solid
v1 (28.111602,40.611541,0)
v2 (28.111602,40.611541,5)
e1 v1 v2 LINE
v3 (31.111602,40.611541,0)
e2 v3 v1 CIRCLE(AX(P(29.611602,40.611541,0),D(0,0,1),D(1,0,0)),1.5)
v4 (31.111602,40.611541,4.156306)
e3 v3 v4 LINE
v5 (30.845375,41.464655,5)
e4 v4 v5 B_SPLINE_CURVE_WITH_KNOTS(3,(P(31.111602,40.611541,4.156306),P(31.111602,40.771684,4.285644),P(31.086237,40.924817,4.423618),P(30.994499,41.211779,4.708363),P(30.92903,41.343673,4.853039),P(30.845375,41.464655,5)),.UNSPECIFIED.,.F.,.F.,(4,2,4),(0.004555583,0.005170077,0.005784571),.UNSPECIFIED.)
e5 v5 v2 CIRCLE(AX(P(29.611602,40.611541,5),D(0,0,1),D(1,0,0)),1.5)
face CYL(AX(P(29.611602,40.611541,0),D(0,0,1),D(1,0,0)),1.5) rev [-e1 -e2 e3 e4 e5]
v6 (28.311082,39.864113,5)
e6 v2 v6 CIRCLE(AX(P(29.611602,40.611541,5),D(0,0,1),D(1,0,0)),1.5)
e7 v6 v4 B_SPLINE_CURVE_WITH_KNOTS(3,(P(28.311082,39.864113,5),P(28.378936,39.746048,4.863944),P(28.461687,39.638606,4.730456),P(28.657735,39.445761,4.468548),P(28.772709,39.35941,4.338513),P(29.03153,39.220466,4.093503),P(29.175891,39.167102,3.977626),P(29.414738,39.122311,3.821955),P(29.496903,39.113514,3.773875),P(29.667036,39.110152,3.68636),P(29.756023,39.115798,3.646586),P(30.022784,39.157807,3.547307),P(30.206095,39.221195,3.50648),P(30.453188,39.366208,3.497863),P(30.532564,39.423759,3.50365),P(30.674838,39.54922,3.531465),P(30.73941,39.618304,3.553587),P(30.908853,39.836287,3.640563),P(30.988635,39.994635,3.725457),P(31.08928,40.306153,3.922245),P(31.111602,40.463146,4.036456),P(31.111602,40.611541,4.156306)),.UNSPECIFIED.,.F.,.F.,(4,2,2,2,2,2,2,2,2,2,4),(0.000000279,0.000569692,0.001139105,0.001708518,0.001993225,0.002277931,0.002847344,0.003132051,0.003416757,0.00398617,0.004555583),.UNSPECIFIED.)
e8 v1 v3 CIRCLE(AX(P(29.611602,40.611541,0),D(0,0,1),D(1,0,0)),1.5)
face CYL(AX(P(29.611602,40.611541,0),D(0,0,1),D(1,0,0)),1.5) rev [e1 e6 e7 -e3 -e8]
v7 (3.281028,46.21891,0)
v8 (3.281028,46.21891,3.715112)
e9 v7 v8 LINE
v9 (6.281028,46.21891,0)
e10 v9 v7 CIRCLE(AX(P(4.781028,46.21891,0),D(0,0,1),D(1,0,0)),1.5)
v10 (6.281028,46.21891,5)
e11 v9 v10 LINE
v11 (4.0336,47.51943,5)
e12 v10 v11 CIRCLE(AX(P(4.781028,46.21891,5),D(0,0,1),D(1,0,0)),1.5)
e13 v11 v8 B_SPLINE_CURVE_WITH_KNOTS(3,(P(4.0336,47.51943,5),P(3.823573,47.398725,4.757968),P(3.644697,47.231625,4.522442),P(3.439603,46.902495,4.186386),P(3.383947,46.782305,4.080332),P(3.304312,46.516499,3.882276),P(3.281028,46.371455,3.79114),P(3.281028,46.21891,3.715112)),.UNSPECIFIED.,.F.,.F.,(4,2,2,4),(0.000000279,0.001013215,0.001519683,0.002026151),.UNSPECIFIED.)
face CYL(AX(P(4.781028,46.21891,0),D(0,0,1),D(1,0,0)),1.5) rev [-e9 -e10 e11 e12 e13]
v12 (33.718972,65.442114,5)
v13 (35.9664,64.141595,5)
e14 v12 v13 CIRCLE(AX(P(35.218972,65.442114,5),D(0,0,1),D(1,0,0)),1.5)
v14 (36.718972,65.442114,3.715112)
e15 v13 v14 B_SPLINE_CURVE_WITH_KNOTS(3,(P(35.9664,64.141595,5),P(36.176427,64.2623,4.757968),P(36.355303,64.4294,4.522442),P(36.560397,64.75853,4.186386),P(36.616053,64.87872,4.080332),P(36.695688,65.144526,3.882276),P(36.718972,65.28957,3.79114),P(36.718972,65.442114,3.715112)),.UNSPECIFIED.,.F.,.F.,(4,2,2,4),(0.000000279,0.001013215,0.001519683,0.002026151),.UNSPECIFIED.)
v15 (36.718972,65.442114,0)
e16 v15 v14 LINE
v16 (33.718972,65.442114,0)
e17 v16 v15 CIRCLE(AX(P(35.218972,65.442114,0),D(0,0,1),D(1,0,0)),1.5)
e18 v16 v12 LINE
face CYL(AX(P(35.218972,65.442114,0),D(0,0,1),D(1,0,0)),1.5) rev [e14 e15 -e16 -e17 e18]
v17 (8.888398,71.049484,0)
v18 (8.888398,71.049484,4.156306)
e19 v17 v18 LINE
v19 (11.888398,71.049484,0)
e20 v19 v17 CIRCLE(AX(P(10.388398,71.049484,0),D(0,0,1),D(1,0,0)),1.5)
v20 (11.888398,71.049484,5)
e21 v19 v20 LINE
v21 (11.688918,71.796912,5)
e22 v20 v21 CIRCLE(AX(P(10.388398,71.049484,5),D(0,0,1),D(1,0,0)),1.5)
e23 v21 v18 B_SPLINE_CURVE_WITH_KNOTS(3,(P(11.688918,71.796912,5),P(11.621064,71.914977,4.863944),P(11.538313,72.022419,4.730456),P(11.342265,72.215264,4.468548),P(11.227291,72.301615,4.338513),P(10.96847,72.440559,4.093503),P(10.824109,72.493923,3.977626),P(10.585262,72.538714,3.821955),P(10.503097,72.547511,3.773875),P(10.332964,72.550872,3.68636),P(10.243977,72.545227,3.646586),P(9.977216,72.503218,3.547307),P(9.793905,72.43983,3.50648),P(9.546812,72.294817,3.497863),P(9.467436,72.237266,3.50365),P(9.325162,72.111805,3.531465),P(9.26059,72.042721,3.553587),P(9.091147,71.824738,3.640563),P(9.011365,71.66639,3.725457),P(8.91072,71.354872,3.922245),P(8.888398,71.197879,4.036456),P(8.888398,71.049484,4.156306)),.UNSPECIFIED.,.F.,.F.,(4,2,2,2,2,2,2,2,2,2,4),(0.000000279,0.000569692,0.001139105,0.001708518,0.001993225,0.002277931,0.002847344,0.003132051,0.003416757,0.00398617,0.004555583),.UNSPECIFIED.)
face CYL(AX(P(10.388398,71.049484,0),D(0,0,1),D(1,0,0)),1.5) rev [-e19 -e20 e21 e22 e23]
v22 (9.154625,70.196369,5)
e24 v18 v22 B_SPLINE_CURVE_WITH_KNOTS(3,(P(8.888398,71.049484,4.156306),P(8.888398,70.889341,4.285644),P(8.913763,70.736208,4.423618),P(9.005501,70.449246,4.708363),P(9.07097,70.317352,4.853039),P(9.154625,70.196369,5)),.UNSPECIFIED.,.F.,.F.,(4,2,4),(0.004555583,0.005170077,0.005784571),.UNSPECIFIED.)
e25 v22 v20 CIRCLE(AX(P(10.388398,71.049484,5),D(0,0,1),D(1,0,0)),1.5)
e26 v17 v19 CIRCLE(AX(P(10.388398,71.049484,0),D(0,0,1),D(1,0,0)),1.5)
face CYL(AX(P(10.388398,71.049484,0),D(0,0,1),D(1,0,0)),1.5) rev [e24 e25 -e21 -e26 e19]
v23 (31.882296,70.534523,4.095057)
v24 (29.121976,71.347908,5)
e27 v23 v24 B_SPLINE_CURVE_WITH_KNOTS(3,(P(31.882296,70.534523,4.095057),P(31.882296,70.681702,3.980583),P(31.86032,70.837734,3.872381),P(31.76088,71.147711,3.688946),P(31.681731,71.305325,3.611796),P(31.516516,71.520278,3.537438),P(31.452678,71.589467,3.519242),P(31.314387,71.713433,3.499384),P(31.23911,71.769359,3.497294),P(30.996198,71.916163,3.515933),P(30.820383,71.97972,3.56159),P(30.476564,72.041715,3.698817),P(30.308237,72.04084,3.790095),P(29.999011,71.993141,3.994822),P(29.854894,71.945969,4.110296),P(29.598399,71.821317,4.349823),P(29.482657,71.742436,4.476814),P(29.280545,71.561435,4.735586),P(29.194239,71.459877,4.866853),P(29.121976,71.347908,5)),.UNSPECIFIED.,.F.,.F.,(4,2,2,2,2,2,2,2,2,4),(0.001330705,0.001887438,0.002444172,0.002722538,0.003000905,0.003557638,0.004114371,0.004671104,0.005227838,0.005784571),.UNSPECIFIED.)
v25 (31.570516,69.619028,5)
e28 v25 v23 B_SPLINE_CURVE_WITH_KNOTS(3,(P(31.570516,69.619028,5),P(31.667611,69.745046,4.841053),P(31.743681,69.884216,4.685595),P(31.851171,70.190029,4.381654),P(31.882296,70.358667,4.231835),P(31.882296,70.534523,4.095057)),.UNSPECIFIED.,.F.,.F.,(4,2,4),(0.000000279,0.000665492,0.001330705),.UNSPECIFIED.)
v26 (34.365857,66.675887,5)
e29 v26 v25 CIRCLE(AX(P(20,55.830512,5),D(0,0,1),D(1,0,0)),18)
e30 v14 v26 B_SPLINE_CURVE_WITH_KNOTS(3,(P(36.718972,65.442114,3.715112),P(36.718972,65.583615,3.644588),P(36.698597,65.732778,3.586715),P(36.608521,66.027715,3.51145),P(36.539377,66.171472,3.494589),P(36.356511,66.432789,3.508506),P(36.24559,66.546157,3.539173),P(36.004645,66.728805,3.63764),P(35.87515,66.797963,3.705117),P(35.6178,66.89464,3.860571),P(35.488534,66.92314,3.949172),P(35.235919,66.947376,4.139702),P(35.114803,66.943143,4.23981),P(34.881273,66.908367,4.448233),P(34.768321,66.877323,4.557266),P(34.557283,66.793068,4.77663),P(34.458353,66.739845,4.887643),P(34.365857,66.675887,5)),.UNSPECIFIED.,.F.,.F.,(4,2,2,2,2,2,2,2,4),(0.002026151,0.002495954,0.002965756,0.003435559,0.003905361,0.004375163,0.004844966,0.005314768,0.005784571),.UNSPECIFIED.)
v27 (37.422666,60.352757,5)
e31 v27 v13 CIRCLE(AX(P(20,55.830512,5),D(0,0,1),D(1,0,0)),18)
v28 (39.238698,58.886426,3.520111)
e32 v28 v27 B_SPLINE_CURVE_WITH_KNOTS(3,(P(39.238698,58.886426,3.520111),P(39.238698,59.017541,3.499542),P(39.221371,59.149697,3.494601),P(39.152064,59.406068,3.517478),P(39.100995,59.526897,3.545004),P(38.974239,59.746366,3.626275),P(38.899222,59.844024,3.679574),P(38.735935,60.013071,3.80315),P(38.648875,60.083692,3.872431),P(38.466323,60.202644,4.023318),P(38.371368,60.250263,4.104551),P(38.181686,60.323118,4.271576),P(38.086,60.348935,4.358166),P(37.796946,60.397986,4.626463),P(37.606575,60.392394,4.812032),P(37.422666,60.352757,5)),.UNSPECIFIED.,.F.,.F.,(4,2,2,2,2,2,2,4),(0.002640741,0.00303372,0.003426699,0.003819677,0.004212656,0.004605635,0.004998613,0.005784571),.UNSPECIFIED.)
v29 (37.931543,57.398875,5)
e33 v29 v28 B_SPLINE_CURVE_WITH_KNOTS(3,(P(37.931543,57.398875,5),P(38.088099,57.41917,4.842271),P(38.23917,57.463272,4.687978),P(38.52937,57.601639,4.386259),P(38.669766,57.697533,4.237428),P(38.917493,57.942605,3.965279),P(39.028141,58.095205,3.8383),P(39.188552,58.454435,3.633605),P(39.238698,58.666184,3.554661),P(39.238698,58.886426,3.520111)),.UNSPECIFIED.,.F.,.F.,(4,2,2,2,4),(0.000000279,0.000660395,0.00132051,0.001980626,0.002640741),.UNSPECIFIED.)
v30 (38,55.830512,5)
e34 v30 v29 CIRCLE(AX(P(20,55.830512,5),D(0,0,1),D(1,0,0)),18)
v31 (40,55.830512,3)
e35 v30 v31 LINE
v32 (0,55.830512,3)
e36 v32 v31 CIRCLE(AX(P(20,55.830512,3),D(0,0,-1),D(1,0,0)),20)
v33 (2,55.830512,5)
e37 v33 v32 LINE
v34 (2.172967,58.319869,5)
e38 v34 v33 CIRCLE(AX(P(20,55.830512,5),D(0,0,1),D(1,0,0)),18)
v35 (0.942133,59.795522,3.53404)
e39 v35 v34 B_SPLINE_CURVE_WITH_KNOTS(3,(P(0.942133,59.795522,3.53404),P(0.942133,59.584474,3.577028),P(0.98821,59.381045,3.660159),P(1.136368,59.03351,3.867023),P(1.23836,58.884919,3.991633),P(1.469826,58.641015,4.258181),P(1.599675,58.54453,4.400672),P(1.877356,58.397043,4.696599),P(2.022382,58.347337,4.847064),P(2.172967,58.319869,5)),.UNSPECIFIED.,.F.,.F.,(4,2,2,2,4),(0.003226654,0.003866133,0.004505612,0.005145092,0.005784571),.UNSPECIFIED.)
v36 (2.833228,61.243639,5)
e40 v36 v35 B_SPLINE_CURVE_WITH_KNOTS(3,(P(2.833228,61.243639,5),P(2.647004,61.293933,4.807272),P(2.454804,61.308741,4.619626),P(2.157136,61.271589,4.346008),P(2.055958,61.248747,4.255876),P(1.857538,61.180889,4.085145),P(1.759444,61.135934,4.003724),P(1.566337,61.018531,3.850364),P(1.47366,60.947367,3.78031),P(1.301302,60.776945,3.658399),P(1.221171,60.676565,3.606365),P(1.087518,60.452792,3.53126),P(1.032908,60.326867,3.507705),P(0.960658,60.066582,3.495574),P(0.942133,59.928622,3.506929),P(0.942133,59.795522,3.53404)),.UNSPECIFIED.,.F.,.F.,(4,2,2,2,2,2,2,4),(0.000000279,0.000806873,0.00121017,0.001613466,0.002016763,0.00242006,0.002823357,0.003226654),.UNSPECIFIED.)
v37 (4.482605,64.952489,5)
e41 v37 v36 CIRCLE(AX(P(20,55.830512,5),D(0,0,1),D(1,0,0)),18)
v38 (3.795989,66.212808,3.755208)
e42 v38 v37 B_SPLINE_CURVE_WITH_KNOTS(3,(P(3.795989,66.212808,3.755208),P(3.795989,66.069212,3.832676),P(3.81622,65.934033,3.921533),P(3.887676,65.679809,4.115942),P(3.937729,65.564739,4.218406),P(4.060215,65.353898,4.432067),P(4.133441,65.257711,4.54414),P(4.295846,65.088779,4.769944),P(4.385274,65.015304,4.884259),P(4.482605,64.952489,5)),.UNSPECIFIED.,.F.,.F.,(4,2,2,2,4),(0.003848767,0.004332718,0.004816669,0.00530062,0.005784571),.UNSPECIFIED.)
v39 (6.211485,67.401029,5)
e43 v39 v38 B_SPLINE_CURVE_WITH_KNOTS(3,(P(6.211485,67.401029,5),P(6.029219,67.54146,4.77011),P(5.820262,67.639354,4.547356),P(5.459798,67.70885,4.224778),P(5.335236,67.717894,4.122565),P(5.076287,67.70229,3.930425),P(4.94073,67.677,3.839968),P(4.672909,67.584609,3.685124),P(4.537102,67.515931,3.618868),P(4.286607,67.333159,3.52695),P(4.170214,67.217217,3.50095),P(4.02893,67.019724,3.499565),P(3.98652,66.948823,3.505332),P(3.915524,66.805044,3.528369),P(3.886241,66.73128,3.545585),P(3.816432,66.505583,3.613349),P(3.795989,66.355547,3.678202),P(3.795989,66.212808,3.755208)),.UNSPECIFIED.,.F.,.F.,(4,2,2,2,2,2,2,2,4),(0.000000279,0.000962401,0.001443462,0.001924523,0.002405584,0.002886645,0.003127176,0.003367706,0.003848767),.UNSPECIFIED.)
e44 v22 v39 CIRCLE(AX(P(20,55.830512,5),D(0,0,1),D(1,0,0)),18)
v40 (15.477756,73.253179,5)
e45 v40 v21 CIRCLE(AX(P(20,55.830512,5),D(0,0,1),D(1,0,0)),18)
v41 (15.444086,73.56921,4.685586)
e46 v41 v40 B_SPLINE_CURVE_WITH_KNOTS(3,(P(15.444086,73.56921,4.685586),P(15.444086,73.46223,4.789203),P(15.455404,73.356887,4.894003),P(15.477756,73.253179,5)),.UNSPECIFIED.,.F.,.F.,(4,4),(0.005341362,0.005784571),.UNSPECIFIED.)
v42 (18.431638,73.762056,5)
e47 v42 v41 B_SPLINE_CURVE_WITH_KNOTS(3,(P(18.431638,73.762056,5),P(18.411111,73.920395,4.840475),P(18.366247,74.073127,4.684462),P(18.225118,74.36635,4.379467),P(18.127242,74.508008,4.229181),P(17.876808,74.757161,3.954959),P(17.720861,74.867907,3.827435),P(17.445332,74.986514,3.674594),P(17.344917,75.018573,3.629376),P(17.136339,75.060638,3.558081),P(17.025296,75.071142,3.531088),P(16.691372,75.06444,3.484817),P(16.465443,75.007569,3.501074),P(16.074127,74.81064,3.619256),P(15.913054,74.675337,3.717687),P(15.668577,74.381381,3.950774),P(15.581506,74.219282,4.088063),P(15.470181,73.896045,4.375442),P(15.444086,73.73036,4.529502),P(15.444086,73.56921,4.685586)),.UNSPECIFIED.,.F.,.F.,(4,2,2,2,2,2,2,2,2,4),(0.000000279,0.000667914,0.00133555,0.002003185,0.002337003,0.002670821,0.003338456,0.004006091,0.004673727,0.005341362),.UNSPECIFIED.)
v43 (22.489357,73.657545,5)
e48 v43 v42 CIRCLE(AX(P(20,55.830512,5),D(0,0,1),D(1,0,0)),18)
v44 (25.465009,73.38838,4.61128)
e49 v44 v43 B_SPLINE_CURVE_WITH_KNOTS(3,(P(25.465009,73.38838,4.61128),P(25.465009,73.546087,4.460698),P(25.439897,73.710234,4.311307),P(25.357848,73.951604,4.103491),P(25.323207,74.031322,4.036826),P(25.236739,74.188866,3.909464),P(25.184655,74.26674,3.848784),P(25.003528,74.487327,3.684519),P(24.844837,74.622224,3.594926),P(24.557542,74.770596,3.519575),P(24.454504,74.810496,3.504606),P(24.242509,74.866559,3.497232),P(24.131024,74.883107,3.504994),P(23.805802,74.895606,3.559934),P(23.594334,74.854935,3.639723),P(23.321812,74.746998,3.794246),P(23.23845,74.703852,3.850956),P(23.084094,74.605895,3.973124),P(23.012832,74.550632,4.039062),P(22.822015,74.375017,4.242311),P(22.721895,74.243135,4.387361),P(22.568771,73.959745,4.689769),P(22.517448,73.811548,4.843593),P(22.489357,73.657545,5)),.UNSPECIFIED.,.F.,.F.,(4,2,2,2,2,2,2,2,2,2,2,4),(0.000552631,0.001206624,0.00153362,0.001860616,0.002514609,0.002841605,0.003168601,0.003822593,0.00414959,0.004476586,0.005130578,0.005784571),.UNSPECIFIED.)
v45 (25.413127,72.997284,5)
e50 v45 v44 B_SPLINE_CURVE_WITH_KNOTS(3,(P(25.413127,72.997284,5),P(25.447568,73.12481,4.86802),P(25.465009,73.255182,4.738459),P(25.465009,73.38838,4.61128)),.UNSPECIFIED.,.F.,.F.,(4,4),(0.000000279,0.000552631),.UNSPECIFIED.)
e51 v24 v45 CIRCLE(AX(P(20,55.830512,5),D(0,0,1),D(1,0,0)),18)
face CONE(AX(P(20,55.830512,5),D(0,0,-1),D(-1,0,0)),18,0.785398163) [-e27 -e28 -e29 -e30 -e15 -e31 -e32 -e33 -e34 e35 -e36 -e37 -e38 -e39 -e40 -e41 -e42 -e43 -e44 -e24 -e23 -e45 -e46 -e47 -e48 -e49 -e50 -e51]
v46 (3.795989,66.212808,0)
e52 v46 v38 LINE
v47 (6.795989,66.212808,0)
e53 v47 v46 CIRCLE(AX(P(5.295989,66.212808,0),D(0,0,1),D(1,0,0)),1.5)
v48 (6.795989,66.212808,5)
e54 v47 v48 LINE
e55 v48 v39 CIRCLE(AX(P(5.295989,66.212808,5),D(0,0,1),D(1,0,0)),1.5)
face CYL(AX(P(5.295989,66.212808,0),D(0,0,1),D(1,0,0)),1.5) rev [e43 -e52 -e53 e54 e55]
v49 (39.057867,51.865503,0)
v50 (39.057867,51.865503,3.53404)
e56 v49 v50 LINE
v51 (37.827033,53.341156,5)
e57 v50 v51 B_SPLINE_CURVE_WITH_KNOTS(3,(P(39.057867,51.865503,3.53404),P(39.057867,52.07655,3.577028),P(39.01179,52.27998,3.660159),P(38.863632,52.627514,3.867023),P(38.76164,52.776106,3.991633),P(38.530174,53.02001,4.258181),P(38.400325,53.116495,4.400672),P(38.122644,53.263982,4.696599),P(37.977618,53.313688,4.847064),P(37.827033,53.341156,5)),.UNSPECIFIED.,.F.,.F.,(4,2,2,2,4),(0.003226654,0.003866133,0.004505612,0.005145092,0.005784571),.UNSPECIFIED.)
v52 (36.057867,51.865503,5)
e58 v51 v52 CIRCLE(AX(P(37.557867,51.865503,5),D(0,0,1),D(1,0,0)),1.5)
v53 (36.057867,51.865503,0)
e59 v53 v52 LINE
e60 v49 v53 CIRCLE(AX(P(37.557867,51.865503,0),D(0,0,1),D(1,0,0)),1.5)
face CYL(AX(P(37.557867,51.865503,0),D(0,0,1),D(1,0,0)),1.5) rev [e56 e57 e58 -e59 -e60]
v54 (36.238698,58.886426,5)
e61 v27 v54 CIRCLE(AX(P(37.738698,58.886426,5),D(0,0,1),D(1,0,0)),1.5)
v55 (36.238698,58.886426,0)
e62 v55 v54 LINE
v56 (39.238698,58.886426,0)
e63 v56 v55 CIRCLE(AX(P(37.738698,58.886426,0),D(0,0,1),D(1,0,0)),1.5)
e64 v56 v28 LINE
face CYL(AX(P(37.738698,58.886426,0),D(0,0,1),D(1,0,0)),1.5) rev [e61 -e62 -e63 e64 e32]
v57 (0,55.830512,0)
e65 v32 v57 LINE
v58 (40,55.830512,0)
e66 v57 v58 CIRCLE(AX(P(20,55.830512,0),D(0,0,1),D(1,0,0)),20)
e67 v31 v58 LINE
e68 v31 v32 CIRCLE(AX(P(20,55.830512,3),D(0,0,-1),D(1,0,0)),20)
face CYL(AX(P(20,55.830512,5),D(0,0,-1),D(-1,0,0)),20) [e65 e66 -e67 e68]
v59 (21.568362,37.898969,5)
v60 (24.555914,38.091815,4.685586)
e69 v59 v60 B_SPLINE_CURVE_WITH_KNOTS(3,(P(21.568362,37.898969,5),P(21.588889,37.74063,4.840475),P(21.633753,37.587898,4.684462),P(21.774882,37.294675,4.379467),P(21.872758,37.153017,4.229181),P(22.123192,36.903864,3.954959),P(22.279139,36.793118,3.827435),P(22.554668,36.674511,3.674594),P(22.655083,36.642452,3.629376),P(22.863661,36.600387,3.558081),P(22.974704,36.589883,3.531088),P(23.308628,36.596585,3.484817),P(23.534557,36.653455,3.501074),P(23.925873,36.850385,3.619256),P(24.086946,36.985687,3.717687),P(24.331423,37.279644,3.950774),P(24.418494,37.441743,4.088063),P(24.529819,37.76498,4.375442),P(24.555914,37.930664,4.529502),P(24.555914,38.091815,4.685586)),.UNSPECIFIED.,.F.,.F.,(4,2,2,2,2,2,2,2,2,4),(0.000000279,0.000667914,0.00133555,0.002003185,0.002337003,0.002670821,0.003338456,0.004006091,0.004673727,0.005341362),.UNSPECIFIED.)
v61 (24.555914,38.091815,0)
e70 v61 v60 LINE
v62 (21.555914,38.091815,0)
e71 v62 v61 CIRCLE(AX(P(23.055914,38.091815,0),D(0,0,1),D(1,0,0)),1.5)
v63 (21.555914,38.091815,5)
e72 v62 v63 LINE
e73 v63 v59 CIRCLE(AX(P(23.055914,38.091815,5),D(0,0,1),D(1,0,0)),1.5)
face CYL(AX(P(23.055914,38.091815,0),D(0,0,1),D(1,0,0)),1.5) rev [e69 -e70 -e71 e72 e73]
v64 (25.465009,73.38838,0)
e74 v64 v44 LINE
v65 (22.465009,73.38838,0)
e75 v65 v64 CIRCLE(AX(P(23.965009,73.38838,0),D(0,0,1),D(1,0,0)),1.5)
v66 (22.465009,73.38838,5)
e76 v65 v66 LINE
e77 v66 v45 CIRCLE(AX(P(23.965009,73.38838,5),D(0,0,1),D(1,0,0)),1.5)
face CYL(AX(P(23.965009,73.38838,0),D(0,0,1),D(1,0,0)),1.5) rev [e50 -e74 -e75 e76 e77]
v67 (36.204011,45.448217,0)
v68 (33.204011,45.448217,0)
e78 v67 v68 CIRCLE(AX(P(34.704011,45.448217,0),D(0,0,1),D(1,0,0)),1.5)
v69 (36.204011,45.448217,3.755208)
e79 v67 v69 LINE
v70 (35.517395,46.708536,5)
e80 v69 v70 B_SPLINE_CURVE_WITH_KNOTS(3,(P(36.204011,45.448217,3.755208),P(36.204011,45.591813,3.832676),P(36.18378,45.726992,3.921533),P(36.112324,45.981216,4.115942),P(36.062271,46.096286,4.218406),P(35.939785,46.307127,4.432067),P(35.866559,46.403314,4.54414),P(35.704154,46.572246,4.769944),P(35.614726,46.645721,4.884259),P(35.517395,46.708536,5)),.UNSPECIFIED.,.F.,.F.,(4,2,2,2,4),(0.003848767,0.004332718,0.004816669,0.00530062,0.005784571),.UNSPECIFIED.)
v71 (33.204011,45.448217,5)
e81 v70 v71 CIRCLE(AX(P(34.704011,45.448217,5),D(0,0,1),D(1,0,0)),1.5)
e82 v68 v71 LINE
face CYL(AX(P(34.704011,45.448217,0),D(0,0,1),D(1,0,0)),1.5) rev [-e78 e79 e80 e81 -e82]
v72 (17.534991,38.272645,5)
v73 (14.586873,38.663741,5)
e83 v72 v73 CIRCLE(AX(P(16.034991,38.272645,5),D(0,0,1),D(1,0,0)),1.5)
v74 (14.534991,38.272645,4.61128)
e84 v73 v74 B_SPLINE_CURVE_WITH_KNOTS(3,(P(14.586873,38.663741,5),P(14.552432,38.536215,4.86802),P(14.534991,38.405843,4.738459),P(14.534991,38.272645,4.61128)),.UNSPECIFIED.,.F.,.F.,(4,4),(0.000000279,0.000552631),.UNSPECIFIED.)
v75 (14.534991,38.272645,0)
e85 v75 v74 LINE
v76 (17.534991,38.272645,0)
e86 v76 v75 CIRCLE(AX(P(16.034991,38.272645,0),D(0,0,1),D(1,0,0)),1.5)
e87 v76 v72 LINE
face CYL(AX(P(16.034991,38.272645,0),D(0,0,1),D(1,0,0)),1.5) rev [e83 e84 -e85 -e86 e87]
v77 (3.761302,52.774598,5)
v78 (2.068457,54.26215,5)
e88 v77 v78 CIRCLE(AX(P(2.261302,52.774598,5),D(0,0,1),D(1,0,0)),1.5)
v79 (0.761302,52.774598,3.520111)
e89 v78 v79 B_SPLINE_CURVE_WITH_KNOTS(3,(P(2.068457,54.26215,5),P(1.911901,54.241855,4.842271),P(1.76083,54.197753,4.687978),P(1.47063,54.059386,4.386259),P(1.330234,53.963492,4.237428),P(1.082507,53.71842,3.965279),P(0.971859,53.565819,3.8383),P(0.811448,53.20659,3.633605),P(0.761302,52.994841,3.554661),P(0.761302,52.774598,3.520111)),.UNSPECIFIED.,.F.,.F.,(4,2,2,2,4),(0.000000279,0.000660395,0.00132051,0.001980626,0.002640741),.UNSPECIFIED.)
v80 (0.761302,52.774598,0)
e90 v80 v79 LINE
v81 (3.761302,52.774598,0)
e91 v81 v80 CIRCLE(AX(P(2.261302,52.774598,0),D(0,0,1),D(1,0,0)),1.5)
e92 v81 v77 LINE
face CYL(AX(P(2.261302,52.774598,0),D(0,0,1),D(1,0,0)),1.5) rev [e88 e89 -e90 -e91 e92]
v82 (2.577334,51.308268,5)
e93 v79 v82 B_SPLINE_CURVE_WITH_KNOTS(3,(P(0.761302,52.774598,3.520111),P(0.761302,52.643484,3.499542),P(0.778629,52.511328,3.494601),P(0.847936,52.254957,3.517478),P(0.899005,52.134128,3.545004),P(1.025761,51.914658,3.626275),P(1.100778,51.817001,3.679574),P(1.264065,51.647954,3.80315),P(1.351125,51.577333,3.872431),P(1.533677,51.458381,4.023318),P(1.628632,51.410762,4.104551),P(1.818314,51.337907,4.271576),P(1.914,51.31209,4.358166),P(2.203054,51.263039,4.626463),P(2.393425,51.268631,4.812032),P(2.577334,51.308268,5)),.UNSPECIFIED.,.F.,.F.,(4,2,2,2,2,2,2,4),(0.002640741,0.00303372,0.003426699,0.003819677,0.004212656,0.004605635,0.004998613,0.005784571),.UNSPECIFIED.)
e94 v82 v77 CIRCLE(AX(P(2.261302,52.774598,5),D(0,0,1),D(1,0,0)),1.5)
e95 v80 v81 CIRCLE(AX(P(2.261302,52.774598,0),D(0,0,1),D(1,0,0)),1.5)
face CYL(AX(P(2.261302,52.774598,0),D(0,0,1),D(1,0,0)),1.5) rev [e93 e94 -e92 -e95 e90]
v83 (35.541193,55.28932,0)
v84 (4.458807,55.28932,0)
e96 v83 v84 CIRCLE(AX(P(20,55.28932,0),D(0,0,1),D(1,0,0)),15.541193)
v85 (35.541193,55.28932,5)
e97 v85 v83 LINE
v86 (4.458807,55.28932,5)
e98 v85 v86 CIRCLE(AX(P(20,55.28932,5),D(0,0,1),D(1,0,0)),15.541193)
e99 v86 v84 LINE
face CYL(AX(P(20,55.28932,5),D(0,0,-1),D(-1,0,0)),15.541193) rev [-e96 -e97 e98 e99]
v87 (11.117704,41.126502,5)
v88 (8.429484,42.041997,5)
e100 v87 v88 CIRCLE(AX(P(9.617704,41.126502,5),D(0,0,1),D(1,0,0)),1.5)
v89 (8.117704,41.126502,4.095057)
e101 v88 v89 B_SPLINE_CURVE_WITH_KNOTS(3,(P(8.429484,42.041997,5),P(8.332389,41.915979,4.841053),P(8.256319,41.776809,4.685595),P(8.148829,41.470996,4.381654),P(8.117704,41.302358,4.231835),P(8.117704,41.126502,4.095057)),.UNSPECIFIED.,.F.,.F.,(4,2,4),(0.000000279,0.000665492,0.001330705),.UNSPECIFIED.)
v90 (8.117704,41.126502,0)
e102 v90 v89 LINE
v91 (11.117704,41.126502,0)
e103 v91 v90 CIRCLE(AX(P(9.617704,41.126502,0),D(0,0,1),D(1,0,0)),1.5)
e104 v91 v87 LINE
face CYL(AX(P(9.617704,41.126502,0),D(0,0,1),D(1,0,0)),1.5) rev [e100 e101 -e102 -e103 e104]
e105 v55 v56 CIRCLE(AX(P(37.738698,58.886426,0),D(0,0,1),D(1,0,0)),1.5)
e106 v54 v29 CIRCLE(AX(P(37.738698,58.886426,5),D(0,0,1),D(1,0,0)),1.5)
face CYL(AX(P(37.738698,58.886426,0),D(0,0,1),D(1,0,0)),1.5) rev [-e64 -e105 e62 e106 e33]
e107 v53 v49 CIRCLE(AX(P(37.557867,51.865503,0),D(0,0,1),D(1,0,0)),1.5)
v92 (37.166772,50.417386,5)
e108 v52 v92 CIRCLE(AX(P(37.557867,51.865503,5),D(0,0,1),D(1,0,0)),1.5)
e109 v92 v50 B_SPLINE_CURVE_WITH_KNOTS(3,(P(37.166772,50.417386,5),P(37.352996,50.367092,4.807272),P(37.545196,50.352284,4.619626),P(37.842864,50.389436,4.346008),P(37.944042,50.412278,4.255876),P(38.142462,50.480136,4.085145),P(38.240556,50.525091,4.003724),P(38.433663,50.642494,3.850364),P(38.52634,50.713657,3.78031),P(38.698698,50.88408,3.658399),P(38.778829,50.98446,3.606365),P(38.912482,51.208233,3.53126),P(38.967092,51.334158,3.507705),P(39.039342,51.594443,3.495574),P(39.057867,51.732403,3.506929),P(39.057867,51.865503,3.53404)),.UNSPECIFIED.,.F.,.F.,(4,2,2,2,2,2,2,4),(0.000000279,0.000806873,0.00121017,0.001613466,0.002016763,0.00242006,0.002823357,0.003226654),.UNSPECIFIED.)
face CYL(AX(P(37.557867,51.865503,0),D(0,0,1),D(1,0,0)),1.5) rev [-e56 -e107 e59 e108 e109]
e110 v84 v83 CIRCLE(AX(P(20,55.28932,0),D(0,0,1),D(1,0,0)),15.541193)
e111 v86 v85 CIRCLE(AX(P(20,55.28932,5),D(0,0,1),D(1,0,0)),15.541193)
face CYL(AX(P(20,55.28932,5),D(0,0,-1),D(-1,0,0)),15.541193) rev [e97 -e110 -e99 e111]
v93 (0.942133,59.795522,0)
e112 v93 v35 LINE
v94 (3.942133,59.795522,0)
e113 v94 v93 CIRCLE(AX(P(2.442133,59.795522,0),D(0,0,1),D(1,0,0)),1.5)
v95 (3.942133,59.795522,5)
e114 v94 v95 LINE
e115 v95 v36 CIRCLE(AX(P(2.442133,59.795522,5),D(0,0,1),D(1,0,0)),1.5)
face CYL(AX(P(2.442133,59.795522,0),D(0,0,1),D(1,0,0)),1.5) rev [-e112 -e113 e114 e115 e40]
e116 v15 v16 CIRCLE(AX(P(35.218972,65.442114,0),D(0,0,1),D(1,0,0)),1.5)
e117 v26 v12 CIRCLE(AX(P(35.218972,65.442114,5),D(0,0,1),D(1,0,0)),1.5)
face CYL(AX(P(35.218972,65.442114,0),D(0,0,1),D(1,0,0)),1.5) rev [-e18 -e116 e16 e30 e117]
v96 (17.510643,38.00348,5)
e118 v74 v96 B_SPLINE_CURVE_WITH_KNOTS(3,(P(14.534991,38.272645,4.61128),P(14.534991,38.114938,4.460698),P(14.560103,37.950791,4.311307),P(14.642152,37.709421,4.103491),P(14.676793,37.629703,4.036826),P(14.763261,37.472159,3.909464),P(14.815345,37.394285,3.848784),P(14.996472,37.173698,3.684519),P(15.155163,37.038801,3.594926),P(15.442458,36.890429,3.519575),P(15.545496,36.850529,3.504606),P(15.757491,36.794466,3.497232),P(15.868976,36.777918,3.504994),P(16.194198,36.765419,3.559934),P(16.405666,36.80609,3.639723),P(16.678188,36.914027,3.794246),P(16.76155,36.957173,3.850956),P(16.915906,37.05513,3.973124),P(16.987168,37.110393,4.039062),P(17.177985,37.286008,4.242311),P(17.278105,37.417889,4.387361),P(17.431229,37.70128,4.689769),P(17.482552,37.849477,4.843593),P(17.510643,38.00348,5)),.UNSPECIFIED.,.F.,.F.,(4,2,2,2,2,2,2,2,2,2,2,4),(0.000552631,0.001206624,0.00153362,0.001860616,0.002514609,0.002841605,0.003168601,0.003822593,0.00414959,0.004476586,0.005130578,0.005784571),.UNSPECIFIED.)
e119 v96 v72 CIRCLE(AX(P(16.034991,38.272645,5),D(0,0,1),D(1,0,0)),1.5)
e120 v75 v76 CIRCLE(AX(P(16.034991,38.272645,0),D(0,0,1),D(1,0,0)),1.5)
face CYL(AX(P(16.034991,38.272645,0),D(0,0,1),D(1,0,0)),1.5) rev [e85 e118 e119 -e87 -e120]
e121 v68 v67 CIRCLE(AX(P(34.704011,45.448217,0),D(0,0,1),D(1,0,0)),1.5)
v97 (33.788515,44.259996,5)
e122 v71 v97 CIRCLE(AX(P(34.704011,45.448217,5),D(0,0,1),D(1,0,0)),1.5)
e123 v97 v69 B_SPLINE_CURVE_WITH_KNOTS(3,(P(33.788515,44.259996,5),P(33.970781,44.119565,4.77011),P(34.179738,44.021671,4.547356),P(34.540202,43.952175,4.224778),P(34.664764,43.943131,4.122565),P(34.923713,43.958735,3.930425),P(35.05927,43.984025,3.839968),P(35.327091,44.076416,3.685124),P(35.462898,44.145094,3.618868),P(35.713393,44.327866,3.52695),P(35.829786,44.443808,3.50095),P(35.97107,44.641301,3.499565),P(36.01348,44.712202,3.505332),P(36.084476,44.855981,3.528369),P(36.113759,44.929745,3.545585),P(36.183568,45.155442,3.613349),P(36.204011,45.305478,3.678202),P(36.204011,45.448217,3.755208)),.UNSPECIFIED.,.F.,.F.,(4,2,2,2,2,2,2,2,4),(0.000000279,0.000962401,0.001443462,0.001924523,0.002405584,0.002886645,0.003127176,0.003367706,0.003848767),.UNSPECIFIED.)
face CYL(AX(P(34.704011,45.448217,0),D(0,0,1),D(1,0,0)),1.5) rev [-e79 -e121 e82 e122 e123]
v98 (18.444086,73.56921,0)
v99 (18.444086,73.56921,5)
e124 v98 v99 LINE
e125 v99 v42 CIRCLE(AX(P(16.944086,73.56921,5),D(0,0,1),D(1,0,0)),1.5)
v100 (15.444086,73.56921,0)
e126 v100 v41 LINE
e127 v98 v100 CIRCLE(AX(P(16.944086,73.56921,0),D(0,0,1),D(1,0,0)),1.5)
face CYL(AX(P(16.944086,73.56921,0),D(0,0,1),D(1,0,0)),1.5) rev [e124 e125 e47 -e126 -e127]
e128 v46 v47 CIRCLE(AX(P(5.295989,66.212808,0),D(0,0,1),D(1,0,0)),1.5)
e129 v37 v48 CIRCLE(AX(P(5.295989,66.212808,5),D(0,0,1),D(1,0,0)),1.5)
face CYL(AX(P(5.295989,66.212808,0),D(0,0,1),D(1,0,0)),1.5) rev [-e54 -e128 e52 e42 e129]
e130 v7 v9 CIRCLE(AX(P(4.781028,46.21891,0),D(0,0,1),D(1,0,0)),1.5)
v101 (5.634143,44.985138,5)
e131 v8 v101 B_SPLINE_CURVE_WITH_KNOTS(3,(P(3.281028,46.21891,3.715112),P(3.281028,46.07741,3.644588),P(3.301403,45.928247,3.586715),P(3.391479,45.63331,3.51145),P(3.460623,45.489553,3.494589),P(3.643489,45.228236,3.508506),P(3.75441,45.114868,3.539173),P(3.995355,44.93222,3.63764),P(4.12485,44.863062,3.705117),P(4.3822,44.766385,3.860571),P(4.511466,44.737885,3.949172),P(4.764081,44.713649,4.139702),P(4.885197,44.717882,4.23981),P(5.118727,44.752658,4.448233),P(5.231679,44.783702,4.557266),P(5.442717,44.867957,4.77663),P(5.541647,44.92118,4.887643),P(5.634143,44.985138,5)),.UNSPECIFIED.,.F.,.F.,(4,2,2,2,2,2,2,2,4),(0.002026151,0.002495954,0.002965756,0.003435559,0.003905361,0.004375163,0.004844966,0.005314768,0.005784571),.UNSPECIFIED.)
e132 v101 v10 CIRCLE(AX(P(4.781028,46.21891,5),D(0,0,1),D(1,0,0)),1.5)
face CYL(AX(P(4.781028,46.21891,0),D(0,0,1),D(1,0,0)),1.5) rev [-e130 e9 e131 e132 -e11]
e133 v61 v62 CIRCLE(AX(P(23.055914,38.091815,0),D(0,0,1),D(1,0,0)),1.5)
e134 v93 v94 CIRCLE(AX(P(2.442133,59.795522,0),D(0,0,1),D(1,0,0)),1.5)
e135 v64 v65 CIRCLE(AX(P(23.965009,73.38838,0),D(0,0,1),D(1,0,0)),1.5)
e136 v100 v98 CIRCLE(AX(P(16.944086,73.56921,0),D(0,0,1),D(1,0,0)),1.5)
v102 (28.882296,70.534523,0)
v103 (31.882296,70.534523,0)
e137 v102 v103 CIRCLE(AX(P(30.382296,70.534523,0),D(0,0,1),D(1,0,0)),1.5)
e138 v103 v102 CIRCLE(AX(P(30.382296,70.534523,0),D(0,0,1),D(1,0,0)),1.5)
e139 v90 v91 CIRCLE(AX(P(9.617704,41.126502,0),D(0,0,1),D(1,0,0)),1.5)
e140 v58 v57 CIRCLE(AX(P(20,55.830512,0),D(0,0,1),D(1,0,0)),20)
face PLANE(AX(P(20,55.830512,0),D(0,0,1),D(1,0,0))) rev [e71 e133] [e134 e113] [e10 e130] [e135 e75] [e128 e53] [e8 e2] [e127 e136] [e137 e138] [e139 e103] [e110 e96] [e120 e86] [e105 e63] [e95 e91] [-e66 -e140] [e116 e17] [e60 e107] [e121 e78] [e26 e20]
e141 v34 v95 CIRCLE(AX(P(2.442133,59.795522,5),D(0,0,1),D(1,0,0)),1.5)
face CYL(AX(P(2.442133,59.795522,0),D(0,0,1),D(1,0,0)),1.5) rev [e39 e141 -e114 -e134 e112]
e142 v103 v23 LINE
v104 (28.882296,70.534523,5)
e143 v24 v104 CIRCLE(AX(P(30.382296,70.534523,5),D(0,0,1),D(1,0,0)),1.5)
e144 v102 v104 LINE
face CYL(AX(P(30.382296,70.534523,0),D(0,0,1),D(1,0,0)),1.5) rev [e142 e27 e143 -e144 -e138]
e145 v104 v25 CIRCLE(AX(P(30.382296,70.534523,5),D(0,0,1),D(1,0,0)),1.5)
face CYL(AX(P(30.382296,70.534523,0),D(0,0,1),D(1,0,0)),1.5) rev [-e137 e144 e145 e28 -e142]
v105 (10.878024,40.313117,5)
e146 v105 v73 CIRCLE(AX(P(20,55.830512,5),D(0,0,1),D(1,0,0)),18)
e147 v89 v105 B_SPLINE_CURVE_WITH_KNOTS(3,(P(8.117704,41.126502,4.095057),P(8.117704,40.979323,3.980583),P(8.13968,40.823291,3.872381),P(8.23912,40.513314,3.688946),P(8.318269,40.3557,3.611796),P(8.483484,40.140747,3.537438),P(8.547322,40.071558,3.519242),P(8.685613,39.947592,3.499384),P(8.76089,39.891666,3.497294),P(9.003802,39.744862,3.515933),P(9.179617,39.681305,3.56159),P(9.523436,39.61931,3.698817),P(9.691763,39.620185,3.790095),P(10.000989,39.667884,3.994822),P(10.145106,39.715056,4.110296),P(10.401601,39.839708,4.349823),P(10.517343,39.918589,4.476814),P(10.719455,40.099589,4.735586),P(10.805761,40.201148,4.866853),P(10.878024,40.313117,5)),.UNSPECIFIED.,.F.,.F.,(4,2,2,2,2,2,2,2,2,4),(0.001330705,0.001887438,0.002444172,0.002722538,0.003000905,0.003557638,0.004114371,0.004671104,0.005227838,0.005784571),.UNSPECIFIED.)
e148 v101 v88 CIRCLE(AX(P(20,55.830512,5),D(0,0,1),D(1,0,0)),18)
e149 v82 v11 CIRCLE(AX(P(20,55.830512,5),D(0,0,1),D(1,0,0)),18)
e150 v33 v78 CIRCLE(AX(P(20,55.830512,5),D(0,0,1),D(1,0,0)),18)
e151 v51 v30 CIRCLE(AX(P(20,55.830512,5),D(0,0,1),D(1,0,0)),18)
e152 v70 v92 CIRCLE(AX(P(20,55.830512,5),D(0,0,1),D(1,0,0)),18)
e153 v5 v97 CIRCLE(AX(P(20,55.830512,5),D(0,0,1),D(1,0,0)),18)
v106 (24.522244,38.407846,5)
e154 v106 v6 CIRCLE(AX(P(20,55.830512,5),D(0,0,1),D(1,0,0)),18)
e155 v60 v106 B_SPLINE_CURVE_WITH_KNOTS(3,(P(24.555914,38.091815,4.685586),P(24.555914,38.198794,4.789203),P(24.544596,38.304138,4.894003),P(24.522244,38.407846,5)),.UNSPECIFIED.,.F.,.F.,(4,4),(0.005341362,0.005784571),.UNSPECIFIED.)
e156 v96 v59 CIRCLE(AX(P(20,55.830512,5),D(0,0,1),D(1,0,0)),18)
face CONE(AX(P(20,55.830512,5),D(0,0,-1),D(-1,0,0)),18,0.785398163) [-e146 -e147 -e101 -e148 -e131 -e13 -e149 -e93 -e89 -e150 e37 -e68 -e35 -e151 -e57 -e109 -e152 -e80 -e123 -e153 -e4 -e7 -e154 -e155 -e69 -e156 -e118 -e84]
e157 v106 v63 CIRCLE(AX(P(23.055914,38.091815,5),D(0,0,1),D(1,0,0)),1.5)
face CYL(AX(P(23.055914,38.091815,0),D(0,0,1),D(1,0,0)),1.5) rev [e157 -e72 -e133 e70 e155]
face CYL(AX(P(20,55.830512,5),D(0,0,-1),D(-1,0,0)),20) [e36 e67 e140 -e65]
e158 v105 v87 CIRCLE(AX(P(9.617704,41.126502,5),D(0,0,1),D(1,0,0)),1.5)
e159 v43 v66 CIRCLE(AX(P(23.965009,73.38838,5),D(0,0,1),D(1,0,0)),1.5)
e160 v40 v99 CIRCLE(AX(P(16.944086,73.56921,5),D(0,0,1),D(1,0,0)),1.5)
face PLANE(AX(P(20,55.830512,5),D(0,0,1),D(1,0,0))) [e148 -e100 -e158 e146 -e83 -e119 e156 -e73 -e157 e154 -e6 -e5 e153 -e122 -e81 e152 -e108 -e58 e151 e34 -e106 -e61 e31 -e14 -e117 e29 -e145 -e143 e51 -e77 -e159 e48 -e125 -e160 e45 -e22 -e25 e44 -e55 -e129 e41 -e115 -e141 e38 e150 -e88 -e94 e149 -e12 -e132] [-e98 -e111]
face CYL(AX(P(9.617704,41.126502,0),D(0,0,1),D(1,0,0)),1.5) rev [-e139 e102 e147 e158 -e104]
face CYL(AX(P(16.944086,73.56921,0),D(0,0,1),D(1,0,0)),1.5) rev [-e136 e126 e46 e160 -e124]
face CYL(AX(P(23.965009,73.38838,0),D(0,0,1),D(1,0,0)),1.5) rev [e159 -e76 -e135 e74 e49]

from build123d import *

# Parameters (mm, degrees)
SKETCH1_R           = 20
SKETCH1_R_2         = 15.541192726
BOSS_EXTRUDE1_DEPTH = 5
CHAMFER1_SIZE       = 2
SKETCH2_R           = 1.5
CUT_EXTRUDE1_DEPTH  = 86.879372487


with BuildPart() as part:
    # Sketch1 → Boss-Extrude1 (new body)
    with BuildSketch(Plane.XY):
        with Locations((20, 55.830512452)):
            Circle(SKETCH1_R)
        with Locations((20, 55.289319726)):
            Circle(SKETCH1_R_2, mode=Mode.SUBTRACT)
    extrude(amount=BOSS_EXTRUDE1_DEPTH)

    # Chamfer1
    chamfer1_edges = [part.edges().sort_by_distance(p)[0] for p in [
        (0, 55.830512452, 5),
    ]]
    chamfer(chamfer1_edges, length=CHAMFER1_SIZE)

    # Sketch2 → Cut-Extrude1 (cut, through all)
    with BuildSketch(Plane.XY.offset(5)):
        with Locations((10.388397973, 71.049484377)):
            Circle(SKETCH2_R)
        with Locations((16.944086026, 73.569209974)):
            Circle(SKETCH2_R)
        with Locations((23.96500928, 73.388379674)):
            Circle(SKETCH2_R)
        with Locations((30.382295814, 70.534523253)):
            Circle(SKETCH2_R)
        with Locations((35.218971926, 65.442114479)):
            Circle(SKETCH2_R)
        with Locations((37.738697522, 58.886426426)):
            Circle(SKETCH2_R)
        with Locations((37.557867223, 51.865503172)):
            Circle(SKETCH2_R)
        with Locations((34.704010801, 45.448216638)):
            Circle(SKETCH2_R)
        with Locations((29.611602027, 40.611540526)):
            Circle(SKETCH2_R)
        with Locations((23.055913974, 38.09181493)):
            Circle(SKETCH2_R)
        with Locations((16.03499072, 38.272645229)):
            Circle(SKETCH2_R)
        with Locations((9.617704186, 41.126501651)):
            Circle(SKETCH2_R)
        with Locations((4.781028074, 46.218910425)):
            Circle(SKETCH2_R)
        with Locations((2.261302478, 52.774598478)):
            Circle(SKETCH2_R)
        with Locations((2.442132777, 59.795521732)):
            Circle(SKETCH2_R)
        with Locations((5.295989199, 66.212808266)):
            Circle(SKETCH2_R)
    extrude(amount=-CUT_EXTRUDE1_DEPTH, mode=Mode.SUBTRACT)


solid = part.part
